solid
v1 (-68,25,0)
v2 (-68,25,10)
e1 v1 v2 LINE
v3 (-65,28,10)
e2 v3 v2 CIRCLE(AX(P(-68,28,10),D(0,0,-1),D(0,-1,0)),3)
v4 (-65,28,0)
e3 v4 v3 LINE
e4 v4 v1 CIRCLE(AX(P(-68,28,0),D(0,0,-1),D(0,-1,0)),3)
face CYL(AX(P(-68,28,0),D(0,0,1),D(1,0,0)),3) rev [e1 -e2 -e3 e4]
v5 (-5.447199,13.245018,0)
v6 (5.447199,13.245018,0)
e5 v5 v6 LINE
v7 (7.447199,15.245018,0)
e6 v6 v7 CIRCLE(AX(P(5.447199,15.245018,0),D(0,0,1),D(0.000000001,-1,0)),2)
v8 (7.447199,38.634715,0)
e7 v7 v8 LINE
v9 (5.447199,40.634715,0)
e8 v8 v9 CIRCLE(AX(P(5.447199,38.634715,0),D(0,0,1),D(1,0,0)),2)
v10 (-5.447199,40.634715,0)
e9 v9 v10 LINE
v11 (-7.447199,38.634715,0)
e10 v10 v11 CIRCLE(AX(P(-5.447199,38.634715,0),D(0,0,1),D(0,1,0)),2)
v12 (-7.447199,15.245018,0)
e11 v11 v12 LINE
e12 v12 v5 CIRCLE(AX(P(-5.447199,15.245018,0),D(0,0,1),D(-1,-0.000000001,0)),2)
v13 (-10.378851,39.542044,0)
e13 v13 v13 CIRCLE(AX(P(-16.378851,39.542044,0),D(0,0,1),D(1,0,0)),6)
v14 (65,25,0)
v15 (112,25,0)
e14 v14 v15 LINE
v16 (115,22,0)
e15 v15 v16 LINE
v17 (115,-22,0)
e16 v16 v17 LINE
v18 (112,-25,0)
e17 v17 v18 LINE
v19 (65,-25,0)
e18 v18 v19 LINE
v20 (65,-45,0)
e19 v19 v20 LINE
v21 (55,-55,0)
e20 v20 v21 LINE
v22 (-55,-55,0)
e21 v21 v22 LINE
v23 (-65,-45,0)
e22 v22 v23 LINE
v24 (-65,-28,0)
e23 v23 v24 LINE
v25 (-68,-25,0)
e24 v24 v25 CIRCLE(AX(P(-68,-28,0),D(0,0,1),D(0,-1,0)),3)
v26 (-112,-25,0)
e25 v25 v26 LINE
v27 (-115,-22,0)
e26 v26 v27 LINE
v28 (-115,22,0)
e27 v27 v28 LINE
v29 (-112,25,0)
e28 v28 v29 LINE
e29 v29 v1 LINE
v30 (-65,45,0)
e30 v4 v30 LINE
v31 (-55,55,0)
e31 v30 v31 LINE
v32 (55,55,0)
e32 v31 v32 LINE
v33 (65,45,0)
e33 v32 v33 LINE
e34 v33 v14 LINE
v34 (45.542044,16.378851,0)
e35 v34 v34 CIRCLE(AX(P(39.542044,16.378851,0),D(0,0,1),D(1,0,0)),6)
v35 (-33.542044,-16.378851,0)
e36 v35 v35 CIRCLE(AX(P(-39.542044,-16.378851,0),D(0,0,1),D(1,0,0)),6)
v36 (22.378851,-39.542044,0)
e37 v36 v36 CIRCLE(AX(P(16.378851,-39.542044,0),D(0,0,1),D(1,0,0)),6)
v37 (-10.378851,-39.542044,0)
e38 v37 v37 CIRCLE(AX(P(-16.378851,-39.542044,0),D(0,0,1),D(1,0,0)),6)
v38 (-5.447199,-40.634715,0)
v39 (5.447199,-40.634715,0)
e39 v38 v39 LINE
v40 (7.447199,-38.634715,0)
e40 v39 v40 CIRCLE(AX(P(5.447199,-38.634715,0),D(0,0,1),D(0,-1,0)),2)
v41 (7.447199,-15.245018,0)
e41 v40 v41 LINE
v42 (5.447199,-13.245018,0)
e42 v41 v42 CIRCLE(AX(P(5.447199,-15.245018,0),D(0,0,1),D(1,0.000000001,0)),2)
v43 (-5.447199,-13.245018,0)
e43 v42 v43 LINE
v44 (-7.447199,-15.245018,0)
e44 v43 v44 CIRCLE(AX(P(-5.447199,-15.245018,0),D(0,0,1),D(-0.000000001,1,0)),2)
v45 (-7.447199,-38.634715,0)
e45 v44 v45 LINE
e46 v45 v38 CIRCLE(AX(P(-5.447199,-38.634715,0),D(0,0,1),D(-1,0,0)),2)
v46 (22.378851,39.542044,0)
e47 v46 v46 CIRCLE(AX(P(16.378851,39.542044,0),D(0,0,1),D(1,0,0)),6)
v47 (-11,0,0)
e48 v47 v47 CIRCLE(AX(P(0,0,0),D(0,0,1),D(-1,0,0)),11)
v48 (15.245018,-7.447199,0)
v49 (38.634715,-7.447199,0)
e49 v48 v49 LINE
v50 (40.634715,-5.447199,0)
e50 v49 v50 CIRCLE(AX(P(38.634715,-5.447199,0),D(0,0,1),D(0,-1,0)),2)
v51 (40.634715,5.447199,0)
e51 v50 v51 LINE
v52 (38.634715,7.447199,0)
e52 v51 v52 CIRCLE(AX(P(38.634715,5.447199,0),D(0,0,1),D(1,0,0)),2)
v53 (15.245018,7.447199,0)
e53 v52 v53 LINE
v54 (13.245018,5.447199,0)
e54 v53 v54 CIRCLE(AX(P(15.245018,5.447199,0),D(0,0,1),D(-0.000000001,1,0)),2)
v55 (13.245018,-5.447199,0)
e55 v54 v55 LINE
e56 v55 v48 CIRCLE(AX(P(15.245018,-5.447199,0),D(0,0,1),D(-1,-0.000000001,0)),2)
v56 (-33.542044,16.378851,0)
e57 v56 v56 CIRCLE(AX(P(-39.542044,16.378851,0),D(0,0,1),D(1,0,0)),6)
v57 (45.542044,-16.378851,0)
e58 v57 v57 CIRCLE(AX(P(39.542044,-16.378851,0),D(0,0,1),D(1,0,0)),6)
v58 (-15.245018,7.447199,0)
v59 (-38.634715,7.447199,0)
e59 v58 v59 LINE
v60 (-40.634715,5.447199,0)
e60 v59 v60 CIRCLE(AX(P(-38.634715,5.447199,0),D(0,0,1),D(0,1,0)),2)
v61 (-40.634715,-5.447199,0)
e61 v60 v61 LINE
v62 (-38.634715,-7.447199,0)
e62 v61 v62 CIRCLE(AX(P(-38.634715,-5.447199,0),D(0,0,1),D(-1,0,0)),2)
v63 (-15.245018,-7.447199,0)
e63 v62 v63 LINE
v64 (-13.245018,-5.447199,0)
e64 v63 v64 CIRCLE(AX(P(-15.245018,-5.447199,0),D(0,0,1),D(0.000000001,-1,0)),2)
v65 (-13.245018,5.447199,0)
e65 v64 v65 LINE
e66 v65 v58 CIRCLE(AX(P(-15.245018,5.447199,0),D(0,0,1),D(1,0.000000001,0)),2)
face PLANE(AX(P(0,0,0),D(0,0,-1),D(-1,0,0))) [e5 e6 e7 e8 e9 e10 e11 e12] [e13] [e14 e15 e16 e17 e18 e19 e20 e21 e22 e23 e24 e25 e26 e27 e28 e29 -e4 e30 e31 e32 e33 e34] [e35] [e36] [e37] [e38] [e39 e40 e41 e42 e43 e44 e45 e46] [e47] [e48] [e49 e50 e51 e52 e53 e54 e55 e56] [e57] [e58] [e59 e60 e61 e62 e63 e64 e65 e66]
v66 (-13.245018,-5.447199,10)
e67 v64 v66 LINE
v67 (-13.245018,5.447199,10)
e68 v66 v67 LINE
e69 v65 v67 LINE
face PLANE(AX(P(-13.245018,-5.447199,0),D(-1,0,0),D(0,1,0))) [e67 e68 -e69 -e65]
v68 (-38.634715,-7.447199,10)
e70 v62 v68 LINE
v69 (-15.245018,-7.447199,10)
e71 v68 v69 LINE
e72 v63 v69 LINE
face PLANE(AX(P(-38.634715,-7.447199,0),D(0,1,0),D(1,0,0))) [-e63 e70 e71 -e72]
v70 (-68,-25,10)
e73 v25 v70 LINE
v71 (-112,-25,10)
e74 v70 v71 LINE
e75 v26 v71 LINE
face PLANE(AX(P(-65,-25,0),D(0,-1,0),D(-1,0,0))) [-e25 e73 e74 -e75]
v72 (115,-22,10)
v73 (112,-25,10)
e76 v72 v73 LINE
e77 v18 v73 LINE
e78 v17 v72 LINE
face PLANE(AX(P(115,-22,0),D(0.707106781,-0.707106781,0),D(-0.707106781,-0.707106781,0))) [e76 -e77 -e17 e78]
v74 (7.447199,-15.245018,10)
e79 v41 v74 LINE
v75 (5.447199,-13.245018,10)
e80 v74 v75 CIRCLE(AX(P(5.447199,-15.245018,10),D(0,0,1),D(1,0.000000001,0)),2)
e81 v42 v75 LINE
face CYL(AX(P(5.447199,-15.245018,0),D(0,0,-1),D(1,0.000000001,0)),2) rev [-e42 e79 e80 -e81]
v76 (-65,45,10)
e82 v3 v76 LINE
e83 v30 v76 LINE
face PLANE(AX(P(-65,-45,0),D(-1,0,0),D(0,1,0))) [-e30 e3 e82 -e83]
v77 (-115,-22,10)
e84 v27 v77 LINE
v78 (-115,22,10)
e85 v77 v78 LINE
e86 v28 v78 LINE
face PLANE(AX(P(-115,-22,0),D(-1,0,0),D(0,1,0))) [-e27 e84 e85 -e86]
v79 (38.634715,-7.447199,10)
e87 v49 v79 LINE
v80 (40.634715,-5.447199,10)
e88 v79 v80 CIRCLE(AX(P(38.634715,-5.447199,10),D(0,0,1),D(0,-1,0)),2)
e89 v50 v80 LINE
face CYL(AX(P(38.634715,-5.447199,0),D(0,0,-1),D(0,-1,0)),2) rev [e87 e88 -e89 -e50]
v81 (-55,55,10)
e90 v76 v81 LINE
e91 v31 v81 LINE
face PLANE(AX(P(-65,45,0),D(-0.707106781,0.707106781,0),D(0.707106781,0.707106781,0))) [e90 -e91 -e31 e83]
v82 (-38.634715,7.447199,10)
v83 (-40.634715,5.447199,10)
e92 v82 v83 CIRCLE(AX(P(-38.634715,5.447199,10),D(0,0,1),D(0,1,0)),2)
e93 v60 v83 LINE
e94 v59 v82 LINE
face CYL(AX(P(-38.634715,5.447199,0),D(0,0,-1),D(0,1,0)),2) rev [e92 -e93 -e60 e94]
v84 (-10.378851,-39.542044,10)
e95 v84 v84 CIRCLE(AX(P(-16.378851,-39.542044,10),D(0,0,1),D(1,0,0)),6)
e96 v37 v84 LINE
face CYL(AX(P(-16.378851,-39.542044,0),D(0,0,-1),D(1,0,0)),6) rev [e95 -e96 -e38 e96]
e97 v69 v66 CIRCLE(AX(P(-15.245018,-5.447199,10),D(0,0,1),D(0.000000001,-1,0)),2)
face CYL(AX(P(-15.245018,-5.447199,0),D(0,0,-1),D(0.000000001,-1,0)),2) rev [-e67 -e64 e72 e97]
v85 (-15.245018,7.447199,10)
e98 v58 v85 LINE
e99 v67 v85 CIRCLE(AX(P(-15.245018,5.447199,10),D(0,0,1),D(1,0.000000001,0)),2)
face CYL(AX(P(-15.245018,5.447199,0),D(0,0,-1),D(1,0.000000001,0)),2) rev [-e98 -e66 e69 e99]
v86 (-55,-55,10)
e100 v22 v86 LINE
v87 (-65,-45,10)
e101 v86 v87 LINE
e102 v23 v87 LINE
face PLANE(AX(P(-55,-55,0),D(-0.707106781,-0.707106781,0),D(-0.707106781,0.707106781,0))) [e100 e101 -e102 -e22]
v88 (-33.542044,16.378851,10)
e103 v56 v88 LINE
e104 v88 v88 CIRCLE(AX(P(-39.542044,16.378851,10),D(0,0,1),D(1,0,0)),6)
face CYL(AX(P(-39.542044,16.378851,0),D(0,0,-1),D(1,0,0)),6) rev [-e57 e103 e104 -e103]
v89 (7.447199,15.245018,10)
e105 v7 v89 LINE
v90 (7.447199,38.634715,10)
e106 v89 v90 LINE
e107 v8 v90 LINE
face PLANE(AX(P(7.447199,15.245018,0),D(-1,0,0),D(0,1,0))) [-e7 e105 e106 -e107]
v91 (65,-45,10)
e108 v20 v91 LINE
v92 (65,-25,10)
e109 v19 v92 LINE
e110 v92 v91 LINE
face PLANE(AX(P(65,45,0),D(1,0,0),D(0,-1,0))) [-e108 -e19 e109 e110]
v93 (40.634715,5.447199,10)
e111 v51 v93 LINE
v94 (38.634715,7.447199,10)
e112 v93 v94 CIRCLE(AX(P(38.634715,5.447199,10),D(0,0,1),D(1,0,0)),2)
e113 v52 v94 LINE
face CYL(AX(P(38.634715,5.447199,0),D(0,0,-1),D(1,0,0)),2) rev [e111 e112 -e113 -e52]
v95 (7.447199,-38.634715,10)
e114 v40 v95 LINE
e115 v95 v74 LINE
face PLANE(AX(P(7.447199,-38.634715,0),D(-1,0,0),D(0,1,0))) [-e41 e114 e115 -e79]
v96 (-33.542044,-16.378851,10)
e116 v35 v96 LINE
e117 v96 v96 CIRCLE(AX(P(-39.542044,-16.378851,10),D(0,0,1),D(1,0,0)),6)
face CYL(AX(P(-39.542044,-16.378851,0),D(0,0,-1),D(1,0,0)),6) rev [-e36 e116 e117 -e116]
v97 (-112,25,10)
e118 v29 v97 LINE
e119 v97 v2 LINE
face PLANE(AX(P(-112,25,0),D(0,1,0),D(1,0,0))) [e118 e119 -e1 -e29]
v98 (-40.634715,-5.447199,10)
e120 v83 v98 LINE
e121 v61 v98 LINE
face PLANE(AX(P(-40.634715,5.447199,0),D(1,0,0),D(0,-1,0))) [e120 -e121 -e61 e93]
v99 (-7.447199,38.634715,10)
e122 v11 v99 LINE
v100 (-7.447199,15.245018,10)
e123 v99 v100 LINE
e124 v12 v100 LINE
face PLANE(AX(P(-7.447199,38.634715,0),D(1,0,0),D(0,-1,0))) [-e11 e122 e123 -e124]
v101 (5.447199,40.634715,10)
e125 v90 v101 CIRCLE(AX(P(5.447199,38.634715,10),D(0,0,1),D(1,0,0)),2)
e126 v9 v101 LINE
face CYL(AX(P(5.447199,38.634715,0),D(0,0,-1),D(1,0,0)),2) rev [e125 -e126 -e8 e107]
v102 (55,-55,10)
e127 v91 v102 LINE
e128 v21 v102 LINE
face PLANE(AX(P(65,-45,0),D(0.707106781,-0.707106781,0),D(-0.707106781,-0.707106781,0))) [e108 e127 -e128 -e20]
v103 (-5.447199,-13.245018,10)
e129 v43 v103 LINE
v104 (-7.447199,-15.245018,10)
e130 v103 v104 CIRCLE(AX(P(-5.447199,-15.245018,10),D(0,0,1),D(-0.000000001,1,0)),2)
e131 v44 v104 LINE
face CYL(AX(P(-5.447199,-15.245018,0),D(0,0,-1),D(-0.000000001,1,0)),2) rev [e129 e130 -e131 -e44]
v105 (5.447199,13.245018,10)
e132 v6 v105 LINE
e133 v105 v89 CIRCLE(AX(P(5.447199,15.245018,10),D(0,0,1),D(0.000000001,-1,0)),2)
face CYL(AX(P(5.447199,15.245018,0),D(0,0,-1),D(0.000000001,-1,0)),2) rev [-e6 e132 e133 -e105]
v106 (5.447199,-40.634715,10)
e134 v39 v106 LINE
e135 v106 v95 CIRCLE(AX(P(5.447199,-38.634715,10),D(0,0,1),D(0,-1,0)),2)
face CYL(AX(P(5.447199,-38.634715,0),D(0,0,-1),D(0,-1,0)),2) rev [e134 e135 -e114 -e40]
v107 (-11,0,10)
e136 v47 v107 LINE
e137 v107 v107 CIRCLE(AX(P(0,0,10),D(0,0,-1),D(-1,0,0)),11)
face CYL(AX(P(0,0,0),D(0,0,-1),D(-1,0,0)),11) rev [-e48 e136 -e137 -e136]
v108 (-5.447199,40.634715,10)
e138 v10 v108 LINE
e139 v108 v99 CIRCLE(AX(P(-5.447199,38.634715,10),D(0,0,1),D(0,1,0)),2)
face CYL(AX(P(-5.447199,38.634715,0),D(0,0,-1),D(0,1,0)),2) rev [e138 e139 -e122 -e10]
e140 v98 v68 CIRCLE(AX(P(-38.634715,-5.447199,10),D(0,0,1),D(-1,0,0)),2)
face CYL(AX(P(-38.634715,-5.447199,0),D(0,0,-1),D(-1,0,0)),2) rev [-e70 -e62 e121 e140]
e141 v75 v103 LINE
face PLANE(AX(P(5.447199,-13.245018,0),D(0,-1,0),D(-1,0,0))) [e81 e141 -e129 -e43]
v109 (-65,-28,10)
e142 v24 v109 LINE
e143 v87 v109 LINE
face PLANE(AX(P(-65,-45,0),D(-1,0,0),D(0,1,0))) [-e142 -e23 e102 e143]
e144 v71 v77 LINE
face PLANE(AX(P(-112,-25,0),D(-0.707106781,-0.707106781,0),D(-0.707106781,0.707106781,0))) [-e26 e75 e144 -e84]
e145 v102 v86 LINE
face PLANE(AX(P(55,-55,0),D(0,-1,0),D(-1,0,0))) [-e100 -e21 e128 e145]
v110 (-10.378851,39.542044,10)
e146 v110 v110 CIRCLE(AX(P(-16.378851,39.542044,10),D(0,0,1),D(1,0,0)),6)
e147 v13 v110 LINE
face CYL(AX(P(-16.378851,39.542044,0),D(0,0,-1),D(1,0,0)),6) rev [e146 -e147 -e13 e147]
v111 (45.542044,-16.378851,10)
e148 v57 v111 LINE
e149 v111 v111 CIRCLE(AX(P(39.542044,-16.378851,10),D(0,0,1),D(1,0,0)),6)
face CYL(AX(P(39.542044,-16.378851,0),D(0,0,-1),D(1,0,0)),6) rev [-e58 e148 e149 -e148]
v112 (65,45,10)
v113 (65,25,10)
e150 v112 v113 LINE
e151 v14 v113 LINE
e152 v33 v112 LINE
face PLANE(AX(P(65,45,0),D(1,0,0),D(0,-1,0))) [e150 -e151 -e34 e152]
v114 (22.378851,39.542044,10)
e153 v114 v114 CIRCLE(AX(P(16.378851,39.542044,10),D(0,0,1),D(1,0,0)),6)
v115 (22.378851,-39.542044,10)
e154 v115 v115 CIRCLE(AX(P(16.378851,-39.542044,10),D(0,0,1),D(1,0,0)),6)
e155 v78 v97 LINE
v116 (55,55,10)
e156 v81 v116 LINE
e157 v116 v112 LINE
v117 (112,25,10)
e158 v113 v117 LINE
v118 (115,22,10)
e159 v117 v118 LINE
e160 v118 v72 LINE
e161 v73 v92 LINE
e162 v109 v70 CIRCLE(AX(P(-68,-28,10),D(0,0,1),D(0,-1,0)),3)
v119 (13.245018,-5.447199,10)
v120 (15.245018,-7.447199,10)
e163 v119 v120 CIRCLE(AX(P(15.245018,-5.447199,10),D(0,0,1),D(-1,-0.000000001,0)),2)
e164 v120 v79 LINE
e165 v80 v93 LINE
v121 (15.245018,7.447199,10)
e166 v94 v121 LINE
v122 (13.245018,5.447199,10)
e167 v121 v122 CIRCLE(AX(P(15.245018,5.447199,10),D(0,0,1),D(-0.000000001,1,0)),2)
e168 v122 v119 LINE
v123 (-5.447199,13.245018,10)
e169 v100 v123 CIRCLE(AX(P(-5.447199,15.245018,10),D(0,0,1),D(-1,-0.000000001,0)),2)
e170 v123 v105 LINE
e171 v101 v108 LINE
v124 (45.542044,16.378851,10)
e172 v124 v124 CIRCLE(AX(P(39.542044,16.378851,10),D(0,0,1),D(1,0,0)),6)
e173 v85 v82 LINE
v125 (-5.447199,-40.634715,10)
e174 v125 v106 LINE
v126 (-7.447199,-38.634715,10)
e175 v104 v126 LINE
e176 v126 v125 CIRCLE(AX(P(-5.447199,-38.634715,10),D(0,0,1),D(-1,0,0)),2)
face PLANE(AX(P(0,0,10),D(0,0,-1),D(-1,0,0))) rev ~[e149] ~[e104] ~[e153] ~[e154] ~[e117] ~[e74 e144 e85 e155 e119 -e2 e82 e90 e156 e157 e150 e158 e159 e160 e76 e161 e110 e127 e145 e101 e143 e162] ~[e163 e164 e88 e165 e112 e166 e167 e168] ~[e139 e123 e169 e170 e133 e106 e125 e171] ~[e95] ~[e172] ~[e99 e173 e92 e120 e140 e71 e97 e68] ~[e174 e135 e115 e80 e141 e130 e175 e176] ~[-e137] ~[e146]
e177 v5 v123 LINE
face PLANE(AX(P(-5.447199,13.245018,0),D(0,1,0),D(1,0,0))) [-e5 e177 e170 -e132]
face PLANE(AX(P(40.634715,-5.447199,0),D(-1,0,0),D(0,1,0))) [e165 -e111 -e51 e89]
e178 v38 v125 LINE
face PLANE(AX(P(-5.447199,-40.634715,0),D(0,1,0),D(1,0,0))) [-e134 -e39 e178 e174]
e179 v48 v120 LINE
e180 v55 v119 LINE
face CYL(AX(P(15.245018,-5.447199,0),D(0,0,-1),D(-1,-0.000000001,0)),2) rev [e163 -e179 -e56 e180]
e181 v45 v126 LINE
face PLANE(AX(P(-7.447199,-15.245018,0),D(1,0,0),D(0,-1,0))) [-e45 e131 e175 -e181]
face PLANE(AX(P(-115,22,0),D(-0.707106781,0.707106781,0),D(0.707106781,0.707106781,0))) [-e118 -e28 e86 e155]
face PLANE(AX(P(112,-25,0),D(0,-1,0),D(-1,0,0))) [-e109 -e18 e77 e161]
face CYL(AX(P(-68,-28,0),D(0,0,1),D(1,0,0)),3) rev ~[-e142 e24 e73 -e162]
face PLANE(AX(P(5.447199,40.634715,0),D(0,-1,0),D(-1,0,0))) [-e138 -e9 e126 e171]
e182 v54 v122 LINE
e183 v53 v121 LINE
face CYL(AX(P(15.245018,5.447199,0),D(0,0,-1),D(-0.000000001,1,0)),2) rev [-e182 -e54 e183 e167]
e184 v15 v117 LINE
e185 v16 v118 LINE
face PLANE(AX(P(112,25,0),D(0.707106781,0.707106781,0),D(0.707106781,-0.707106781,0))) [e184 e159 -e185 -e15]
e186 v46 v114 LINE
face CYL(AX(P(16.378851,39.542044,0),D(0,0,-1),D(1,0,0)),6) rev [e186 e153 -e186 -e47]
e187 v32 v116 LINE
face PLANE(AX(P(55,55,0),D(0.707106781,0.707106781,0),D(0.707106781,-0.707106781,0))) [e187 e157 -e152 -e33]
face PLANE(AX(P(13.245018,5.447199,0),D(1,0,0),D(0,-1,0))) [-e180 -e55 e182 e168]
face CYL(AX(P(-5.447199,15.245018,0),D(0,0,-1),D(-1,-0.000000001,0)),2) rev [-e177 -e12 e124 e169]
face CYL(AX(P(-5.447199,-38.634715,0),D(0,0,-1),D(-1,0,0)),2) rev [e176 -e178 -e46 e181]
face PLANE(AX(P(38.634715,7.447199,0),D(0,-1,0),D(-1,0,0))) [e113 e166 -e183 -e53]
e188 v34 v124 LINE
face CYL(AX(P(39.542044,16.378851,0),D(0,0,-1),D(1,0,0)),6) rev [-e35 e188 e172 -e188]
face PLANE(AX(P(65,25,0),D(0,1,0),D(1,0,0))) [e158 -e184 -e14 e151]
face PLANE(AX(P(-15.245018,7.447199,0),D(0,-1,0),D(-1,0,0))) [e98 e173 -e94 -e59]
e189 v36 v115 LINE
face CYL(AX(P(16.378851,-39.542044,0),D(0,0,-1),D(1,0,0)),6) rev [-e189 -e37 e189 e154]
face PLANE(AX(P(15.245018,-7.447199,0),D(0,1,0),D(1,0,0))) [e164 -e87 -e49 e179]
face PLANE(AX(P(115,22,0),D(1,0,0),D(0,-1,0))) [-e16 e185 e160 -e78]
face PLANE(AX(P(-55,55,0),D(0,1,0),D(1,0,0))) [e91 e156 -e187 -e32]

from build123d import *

# Parameters (mm, degrees)
SKETCH1_R               = 6
BOSS_EXTRUDE1_DEPTH     = 10
BOSS_EXTRUDE2_DEPTH     = 10
FILLET1_R               = 3
CUT_EXTRUDE1_DEPTH      = 128.867118525
CUT_EXTRUDE1_DEPTH_BACK = 10
SKETCH3_R               = 11


with BuildPart() as part:
    # Sketch1 → Boss-Extrude1 (new body)
    with BuildSketch(Plane.XY):
        Polygon((-65, 45), (-55, 55), (55, 55), (65, 45), (65, -45), (55, -55), (-55, -55), (-65, -45), align=None)
        with Locations((16.378850905, 39.542043991)):
            Circle(SKETCH1_R, mode=Mode.SUBTRACT)
        with Locations((39.542043991, 16.378850905)):
            Circle(SKETCH1_R, mode=Mode.SUBTRACT)
        with Locations((39.542043991, -16.378850905)):
            Circle(SKETCH1_R, mode=Mode.SUBTRACT)
        with Locations((16.378850905, -39.542043991)):
            Circle(SKETCH1_R, mode=Mode.SUBTRACT)
        with Locations((-16.378850905, -39.542043991)):
            Circle(SKETCH1_R, mode=Mode.SUBTRACT)
        with Locations((-39.542043991, -16.378850905)):
            Circle(SKETCH1_R, mode=Mode.SUBTRACT)
        with Locations((-39.542043991, 16.378850905)):
            Circle(SKETCH1_R, mode=Mode.SUBTRACT)
        with Locations((-16.378850905, 39.542043991)):
            Circle(SKETCH1_R, mode=Mode.SUBTRACT)
        with BuildLine():
            Line((5.447198752, 40.634715337), (-5.447198752, 40.634715337))
            ThreePointArc((-5.447198752, 40.634715337), (-6.861412314, 40.0489289), (-7.447198752, 38.634715337))
            Line((-7.447198752, 38.634715337), (-7.447198752, 15.245017914))
            ThreePointArc((-7.447198752, 15.245017914), (-6.861412314, 13.830804352), (-5.447198752, 13.245017914))
            Line((-5.447198752, 13.245017914), (5.447198752, 13.245017914))
            ThreePointArc((5.447198752, 13.245017914), (6.861412314, 13.830804352), (7.447198752, 15.245017914))
            Line((7.447198752, 15.245017914), (7.447198752, 38.634715337))
            ThreePointArc((7.447198752, 38.634715337), (6.861412314, 40.0489289), (5.447198752, 40.634715337))
        make_face(mode=Mode.SUBTRACT)
        with BuildLine():
            Line((15.245017914, -7.447198752), (38.634715337, -7.447198752))
            ThreePointArc((38.634715337, -7.447198752), (40.0489289, -6.861412314), (40.634715337, -5.447198752))
            Line((40.634715337, -5.447198752), (40.634715337, 5.447198752))
            ThreePointArc((40.634715337, 5.447198752), (40.0489289, 6.861412314), (38.634715337, 7.447198752))
            Line((38.634715337, 7.447198752), (15.245017914, 7.447198752))
            ThreePointArc((15.245017914, 7.447198752), (13.830804352, 6.861412314), (13.245017914, 5.447198752))
            Line((13.245017914, 5.447198752), (13.245017914, -5.447198752))
            ThreePointArc((13.245017914, -5.447198752), (13.830804352, -6.861412314), (15.245017914, -7.447198752))
        make_face(mode=Mode.SUBTRACT)
        with BuildLine():
            Line((-7.447198752, -15.245017914), (-7.447198752, -38.634715337))
            ThreePointArc((-7.447198752, -38.634715337), (-6.861412314, -40.0489289), (-5.447198752, -40.634715337))
            Line((-5.447198752, -40.634715337), (5.447198752, -40.634715337))
            ThreePointArc((5.447198752, -40.634715337), (6.861412314, -40.0489289), (7.447198752, -38.634715337))
            Line((7.447198752, -38.634715337), (7.447198752, -15.245017914))
            ThreePointArc((7.447198752, -15.245017914), (6.861412314, -13.830804352), (5.447198752, -13.245017914))
            Line((5.447198752, -13.245017914), (-5.447198752, -13.245017914))
            ThreePointArc((-5.447198752, -13.245017914), (-6.861412314, -13.830804352), (-7.447198752, -15.245017914))
        make_face(mode=Mode.SUBTRACT)
        with BuildLine():
            Line((-15.245017914, 7.447198752), (-38.634715337, 7.447198752))
            ThreePointArc((-38.634715337, 7.447198752), (-40.0489289, 6.861412314), (-40.634715337, 5.447198752))
            Line((-40.634715337, 5.447198752), (-40.634715337, -5.447198752))
            ThreePointArc((-40.634715337, -5.447198752), (-40.0489289, -6.861412314), (-38.634715337, -7.447198752))
            Line((-38.634715337, -7.447198752), (-15.245017914, -7.447198752))
            ThreePointArc((-15.245017914, -7.447198752), (-13.830804352, -6.861412314), (-13.245017914, -5.447198752))
            Line((-13.245017914, -5.447198752), (-13.245017914, 5.447198752))
            ThreePointArc((-13.245017914, 5.447198752), (-13.830804352, 6.861412314), (-15.245017914, 7.447198752))
        make_face(mode=Mode.SUBTRACT)
    extrude(amount=BOSS_EXTRUDE1_DEPTH)

    # Sketch2 → Boss-Extrude2 (add)
    with BuildSketch(Plane.XY):
        Polygon((-112, 25), (-65, 25), (-65, -25), (-112, -25), (-115, -22), (-115, 22), align=None)
        Polygon((115, -22), (112, -25), (65, -25), (65, 25), (112, 25), (115, 22), align=None)
    extrude(amount=BOSS_EXTRUDE2_DEPTH)

    # Fillet1
    fillet1_edges = [part.edges().sort_by_distance(p)[0] for p in [
        (-65, 25, 5),
        (-65, -25, 5),
    ]]
    fillet(fillet1_edges, radius=FILLET1_R)

    # Sketch3 → Cut-Extrude1 (cut, two sides: drawn at the far end of the back side and taken through both)
    with BuildSketch(Plane.XY.offset(10).offset(-CUT_EXTRUDE1_DEPTH_BACK)):
        with Locations(Location((0, 0, 0), (0, 0, 180))):
            Circle(SKETCH3_R)
    extrude(amount=CUT_EXTRUDE1_DEPTH + CUT_EXTRUDE1_DEPTH_BACK, mode=Mode.SUBTRACT)


solid = part.part
